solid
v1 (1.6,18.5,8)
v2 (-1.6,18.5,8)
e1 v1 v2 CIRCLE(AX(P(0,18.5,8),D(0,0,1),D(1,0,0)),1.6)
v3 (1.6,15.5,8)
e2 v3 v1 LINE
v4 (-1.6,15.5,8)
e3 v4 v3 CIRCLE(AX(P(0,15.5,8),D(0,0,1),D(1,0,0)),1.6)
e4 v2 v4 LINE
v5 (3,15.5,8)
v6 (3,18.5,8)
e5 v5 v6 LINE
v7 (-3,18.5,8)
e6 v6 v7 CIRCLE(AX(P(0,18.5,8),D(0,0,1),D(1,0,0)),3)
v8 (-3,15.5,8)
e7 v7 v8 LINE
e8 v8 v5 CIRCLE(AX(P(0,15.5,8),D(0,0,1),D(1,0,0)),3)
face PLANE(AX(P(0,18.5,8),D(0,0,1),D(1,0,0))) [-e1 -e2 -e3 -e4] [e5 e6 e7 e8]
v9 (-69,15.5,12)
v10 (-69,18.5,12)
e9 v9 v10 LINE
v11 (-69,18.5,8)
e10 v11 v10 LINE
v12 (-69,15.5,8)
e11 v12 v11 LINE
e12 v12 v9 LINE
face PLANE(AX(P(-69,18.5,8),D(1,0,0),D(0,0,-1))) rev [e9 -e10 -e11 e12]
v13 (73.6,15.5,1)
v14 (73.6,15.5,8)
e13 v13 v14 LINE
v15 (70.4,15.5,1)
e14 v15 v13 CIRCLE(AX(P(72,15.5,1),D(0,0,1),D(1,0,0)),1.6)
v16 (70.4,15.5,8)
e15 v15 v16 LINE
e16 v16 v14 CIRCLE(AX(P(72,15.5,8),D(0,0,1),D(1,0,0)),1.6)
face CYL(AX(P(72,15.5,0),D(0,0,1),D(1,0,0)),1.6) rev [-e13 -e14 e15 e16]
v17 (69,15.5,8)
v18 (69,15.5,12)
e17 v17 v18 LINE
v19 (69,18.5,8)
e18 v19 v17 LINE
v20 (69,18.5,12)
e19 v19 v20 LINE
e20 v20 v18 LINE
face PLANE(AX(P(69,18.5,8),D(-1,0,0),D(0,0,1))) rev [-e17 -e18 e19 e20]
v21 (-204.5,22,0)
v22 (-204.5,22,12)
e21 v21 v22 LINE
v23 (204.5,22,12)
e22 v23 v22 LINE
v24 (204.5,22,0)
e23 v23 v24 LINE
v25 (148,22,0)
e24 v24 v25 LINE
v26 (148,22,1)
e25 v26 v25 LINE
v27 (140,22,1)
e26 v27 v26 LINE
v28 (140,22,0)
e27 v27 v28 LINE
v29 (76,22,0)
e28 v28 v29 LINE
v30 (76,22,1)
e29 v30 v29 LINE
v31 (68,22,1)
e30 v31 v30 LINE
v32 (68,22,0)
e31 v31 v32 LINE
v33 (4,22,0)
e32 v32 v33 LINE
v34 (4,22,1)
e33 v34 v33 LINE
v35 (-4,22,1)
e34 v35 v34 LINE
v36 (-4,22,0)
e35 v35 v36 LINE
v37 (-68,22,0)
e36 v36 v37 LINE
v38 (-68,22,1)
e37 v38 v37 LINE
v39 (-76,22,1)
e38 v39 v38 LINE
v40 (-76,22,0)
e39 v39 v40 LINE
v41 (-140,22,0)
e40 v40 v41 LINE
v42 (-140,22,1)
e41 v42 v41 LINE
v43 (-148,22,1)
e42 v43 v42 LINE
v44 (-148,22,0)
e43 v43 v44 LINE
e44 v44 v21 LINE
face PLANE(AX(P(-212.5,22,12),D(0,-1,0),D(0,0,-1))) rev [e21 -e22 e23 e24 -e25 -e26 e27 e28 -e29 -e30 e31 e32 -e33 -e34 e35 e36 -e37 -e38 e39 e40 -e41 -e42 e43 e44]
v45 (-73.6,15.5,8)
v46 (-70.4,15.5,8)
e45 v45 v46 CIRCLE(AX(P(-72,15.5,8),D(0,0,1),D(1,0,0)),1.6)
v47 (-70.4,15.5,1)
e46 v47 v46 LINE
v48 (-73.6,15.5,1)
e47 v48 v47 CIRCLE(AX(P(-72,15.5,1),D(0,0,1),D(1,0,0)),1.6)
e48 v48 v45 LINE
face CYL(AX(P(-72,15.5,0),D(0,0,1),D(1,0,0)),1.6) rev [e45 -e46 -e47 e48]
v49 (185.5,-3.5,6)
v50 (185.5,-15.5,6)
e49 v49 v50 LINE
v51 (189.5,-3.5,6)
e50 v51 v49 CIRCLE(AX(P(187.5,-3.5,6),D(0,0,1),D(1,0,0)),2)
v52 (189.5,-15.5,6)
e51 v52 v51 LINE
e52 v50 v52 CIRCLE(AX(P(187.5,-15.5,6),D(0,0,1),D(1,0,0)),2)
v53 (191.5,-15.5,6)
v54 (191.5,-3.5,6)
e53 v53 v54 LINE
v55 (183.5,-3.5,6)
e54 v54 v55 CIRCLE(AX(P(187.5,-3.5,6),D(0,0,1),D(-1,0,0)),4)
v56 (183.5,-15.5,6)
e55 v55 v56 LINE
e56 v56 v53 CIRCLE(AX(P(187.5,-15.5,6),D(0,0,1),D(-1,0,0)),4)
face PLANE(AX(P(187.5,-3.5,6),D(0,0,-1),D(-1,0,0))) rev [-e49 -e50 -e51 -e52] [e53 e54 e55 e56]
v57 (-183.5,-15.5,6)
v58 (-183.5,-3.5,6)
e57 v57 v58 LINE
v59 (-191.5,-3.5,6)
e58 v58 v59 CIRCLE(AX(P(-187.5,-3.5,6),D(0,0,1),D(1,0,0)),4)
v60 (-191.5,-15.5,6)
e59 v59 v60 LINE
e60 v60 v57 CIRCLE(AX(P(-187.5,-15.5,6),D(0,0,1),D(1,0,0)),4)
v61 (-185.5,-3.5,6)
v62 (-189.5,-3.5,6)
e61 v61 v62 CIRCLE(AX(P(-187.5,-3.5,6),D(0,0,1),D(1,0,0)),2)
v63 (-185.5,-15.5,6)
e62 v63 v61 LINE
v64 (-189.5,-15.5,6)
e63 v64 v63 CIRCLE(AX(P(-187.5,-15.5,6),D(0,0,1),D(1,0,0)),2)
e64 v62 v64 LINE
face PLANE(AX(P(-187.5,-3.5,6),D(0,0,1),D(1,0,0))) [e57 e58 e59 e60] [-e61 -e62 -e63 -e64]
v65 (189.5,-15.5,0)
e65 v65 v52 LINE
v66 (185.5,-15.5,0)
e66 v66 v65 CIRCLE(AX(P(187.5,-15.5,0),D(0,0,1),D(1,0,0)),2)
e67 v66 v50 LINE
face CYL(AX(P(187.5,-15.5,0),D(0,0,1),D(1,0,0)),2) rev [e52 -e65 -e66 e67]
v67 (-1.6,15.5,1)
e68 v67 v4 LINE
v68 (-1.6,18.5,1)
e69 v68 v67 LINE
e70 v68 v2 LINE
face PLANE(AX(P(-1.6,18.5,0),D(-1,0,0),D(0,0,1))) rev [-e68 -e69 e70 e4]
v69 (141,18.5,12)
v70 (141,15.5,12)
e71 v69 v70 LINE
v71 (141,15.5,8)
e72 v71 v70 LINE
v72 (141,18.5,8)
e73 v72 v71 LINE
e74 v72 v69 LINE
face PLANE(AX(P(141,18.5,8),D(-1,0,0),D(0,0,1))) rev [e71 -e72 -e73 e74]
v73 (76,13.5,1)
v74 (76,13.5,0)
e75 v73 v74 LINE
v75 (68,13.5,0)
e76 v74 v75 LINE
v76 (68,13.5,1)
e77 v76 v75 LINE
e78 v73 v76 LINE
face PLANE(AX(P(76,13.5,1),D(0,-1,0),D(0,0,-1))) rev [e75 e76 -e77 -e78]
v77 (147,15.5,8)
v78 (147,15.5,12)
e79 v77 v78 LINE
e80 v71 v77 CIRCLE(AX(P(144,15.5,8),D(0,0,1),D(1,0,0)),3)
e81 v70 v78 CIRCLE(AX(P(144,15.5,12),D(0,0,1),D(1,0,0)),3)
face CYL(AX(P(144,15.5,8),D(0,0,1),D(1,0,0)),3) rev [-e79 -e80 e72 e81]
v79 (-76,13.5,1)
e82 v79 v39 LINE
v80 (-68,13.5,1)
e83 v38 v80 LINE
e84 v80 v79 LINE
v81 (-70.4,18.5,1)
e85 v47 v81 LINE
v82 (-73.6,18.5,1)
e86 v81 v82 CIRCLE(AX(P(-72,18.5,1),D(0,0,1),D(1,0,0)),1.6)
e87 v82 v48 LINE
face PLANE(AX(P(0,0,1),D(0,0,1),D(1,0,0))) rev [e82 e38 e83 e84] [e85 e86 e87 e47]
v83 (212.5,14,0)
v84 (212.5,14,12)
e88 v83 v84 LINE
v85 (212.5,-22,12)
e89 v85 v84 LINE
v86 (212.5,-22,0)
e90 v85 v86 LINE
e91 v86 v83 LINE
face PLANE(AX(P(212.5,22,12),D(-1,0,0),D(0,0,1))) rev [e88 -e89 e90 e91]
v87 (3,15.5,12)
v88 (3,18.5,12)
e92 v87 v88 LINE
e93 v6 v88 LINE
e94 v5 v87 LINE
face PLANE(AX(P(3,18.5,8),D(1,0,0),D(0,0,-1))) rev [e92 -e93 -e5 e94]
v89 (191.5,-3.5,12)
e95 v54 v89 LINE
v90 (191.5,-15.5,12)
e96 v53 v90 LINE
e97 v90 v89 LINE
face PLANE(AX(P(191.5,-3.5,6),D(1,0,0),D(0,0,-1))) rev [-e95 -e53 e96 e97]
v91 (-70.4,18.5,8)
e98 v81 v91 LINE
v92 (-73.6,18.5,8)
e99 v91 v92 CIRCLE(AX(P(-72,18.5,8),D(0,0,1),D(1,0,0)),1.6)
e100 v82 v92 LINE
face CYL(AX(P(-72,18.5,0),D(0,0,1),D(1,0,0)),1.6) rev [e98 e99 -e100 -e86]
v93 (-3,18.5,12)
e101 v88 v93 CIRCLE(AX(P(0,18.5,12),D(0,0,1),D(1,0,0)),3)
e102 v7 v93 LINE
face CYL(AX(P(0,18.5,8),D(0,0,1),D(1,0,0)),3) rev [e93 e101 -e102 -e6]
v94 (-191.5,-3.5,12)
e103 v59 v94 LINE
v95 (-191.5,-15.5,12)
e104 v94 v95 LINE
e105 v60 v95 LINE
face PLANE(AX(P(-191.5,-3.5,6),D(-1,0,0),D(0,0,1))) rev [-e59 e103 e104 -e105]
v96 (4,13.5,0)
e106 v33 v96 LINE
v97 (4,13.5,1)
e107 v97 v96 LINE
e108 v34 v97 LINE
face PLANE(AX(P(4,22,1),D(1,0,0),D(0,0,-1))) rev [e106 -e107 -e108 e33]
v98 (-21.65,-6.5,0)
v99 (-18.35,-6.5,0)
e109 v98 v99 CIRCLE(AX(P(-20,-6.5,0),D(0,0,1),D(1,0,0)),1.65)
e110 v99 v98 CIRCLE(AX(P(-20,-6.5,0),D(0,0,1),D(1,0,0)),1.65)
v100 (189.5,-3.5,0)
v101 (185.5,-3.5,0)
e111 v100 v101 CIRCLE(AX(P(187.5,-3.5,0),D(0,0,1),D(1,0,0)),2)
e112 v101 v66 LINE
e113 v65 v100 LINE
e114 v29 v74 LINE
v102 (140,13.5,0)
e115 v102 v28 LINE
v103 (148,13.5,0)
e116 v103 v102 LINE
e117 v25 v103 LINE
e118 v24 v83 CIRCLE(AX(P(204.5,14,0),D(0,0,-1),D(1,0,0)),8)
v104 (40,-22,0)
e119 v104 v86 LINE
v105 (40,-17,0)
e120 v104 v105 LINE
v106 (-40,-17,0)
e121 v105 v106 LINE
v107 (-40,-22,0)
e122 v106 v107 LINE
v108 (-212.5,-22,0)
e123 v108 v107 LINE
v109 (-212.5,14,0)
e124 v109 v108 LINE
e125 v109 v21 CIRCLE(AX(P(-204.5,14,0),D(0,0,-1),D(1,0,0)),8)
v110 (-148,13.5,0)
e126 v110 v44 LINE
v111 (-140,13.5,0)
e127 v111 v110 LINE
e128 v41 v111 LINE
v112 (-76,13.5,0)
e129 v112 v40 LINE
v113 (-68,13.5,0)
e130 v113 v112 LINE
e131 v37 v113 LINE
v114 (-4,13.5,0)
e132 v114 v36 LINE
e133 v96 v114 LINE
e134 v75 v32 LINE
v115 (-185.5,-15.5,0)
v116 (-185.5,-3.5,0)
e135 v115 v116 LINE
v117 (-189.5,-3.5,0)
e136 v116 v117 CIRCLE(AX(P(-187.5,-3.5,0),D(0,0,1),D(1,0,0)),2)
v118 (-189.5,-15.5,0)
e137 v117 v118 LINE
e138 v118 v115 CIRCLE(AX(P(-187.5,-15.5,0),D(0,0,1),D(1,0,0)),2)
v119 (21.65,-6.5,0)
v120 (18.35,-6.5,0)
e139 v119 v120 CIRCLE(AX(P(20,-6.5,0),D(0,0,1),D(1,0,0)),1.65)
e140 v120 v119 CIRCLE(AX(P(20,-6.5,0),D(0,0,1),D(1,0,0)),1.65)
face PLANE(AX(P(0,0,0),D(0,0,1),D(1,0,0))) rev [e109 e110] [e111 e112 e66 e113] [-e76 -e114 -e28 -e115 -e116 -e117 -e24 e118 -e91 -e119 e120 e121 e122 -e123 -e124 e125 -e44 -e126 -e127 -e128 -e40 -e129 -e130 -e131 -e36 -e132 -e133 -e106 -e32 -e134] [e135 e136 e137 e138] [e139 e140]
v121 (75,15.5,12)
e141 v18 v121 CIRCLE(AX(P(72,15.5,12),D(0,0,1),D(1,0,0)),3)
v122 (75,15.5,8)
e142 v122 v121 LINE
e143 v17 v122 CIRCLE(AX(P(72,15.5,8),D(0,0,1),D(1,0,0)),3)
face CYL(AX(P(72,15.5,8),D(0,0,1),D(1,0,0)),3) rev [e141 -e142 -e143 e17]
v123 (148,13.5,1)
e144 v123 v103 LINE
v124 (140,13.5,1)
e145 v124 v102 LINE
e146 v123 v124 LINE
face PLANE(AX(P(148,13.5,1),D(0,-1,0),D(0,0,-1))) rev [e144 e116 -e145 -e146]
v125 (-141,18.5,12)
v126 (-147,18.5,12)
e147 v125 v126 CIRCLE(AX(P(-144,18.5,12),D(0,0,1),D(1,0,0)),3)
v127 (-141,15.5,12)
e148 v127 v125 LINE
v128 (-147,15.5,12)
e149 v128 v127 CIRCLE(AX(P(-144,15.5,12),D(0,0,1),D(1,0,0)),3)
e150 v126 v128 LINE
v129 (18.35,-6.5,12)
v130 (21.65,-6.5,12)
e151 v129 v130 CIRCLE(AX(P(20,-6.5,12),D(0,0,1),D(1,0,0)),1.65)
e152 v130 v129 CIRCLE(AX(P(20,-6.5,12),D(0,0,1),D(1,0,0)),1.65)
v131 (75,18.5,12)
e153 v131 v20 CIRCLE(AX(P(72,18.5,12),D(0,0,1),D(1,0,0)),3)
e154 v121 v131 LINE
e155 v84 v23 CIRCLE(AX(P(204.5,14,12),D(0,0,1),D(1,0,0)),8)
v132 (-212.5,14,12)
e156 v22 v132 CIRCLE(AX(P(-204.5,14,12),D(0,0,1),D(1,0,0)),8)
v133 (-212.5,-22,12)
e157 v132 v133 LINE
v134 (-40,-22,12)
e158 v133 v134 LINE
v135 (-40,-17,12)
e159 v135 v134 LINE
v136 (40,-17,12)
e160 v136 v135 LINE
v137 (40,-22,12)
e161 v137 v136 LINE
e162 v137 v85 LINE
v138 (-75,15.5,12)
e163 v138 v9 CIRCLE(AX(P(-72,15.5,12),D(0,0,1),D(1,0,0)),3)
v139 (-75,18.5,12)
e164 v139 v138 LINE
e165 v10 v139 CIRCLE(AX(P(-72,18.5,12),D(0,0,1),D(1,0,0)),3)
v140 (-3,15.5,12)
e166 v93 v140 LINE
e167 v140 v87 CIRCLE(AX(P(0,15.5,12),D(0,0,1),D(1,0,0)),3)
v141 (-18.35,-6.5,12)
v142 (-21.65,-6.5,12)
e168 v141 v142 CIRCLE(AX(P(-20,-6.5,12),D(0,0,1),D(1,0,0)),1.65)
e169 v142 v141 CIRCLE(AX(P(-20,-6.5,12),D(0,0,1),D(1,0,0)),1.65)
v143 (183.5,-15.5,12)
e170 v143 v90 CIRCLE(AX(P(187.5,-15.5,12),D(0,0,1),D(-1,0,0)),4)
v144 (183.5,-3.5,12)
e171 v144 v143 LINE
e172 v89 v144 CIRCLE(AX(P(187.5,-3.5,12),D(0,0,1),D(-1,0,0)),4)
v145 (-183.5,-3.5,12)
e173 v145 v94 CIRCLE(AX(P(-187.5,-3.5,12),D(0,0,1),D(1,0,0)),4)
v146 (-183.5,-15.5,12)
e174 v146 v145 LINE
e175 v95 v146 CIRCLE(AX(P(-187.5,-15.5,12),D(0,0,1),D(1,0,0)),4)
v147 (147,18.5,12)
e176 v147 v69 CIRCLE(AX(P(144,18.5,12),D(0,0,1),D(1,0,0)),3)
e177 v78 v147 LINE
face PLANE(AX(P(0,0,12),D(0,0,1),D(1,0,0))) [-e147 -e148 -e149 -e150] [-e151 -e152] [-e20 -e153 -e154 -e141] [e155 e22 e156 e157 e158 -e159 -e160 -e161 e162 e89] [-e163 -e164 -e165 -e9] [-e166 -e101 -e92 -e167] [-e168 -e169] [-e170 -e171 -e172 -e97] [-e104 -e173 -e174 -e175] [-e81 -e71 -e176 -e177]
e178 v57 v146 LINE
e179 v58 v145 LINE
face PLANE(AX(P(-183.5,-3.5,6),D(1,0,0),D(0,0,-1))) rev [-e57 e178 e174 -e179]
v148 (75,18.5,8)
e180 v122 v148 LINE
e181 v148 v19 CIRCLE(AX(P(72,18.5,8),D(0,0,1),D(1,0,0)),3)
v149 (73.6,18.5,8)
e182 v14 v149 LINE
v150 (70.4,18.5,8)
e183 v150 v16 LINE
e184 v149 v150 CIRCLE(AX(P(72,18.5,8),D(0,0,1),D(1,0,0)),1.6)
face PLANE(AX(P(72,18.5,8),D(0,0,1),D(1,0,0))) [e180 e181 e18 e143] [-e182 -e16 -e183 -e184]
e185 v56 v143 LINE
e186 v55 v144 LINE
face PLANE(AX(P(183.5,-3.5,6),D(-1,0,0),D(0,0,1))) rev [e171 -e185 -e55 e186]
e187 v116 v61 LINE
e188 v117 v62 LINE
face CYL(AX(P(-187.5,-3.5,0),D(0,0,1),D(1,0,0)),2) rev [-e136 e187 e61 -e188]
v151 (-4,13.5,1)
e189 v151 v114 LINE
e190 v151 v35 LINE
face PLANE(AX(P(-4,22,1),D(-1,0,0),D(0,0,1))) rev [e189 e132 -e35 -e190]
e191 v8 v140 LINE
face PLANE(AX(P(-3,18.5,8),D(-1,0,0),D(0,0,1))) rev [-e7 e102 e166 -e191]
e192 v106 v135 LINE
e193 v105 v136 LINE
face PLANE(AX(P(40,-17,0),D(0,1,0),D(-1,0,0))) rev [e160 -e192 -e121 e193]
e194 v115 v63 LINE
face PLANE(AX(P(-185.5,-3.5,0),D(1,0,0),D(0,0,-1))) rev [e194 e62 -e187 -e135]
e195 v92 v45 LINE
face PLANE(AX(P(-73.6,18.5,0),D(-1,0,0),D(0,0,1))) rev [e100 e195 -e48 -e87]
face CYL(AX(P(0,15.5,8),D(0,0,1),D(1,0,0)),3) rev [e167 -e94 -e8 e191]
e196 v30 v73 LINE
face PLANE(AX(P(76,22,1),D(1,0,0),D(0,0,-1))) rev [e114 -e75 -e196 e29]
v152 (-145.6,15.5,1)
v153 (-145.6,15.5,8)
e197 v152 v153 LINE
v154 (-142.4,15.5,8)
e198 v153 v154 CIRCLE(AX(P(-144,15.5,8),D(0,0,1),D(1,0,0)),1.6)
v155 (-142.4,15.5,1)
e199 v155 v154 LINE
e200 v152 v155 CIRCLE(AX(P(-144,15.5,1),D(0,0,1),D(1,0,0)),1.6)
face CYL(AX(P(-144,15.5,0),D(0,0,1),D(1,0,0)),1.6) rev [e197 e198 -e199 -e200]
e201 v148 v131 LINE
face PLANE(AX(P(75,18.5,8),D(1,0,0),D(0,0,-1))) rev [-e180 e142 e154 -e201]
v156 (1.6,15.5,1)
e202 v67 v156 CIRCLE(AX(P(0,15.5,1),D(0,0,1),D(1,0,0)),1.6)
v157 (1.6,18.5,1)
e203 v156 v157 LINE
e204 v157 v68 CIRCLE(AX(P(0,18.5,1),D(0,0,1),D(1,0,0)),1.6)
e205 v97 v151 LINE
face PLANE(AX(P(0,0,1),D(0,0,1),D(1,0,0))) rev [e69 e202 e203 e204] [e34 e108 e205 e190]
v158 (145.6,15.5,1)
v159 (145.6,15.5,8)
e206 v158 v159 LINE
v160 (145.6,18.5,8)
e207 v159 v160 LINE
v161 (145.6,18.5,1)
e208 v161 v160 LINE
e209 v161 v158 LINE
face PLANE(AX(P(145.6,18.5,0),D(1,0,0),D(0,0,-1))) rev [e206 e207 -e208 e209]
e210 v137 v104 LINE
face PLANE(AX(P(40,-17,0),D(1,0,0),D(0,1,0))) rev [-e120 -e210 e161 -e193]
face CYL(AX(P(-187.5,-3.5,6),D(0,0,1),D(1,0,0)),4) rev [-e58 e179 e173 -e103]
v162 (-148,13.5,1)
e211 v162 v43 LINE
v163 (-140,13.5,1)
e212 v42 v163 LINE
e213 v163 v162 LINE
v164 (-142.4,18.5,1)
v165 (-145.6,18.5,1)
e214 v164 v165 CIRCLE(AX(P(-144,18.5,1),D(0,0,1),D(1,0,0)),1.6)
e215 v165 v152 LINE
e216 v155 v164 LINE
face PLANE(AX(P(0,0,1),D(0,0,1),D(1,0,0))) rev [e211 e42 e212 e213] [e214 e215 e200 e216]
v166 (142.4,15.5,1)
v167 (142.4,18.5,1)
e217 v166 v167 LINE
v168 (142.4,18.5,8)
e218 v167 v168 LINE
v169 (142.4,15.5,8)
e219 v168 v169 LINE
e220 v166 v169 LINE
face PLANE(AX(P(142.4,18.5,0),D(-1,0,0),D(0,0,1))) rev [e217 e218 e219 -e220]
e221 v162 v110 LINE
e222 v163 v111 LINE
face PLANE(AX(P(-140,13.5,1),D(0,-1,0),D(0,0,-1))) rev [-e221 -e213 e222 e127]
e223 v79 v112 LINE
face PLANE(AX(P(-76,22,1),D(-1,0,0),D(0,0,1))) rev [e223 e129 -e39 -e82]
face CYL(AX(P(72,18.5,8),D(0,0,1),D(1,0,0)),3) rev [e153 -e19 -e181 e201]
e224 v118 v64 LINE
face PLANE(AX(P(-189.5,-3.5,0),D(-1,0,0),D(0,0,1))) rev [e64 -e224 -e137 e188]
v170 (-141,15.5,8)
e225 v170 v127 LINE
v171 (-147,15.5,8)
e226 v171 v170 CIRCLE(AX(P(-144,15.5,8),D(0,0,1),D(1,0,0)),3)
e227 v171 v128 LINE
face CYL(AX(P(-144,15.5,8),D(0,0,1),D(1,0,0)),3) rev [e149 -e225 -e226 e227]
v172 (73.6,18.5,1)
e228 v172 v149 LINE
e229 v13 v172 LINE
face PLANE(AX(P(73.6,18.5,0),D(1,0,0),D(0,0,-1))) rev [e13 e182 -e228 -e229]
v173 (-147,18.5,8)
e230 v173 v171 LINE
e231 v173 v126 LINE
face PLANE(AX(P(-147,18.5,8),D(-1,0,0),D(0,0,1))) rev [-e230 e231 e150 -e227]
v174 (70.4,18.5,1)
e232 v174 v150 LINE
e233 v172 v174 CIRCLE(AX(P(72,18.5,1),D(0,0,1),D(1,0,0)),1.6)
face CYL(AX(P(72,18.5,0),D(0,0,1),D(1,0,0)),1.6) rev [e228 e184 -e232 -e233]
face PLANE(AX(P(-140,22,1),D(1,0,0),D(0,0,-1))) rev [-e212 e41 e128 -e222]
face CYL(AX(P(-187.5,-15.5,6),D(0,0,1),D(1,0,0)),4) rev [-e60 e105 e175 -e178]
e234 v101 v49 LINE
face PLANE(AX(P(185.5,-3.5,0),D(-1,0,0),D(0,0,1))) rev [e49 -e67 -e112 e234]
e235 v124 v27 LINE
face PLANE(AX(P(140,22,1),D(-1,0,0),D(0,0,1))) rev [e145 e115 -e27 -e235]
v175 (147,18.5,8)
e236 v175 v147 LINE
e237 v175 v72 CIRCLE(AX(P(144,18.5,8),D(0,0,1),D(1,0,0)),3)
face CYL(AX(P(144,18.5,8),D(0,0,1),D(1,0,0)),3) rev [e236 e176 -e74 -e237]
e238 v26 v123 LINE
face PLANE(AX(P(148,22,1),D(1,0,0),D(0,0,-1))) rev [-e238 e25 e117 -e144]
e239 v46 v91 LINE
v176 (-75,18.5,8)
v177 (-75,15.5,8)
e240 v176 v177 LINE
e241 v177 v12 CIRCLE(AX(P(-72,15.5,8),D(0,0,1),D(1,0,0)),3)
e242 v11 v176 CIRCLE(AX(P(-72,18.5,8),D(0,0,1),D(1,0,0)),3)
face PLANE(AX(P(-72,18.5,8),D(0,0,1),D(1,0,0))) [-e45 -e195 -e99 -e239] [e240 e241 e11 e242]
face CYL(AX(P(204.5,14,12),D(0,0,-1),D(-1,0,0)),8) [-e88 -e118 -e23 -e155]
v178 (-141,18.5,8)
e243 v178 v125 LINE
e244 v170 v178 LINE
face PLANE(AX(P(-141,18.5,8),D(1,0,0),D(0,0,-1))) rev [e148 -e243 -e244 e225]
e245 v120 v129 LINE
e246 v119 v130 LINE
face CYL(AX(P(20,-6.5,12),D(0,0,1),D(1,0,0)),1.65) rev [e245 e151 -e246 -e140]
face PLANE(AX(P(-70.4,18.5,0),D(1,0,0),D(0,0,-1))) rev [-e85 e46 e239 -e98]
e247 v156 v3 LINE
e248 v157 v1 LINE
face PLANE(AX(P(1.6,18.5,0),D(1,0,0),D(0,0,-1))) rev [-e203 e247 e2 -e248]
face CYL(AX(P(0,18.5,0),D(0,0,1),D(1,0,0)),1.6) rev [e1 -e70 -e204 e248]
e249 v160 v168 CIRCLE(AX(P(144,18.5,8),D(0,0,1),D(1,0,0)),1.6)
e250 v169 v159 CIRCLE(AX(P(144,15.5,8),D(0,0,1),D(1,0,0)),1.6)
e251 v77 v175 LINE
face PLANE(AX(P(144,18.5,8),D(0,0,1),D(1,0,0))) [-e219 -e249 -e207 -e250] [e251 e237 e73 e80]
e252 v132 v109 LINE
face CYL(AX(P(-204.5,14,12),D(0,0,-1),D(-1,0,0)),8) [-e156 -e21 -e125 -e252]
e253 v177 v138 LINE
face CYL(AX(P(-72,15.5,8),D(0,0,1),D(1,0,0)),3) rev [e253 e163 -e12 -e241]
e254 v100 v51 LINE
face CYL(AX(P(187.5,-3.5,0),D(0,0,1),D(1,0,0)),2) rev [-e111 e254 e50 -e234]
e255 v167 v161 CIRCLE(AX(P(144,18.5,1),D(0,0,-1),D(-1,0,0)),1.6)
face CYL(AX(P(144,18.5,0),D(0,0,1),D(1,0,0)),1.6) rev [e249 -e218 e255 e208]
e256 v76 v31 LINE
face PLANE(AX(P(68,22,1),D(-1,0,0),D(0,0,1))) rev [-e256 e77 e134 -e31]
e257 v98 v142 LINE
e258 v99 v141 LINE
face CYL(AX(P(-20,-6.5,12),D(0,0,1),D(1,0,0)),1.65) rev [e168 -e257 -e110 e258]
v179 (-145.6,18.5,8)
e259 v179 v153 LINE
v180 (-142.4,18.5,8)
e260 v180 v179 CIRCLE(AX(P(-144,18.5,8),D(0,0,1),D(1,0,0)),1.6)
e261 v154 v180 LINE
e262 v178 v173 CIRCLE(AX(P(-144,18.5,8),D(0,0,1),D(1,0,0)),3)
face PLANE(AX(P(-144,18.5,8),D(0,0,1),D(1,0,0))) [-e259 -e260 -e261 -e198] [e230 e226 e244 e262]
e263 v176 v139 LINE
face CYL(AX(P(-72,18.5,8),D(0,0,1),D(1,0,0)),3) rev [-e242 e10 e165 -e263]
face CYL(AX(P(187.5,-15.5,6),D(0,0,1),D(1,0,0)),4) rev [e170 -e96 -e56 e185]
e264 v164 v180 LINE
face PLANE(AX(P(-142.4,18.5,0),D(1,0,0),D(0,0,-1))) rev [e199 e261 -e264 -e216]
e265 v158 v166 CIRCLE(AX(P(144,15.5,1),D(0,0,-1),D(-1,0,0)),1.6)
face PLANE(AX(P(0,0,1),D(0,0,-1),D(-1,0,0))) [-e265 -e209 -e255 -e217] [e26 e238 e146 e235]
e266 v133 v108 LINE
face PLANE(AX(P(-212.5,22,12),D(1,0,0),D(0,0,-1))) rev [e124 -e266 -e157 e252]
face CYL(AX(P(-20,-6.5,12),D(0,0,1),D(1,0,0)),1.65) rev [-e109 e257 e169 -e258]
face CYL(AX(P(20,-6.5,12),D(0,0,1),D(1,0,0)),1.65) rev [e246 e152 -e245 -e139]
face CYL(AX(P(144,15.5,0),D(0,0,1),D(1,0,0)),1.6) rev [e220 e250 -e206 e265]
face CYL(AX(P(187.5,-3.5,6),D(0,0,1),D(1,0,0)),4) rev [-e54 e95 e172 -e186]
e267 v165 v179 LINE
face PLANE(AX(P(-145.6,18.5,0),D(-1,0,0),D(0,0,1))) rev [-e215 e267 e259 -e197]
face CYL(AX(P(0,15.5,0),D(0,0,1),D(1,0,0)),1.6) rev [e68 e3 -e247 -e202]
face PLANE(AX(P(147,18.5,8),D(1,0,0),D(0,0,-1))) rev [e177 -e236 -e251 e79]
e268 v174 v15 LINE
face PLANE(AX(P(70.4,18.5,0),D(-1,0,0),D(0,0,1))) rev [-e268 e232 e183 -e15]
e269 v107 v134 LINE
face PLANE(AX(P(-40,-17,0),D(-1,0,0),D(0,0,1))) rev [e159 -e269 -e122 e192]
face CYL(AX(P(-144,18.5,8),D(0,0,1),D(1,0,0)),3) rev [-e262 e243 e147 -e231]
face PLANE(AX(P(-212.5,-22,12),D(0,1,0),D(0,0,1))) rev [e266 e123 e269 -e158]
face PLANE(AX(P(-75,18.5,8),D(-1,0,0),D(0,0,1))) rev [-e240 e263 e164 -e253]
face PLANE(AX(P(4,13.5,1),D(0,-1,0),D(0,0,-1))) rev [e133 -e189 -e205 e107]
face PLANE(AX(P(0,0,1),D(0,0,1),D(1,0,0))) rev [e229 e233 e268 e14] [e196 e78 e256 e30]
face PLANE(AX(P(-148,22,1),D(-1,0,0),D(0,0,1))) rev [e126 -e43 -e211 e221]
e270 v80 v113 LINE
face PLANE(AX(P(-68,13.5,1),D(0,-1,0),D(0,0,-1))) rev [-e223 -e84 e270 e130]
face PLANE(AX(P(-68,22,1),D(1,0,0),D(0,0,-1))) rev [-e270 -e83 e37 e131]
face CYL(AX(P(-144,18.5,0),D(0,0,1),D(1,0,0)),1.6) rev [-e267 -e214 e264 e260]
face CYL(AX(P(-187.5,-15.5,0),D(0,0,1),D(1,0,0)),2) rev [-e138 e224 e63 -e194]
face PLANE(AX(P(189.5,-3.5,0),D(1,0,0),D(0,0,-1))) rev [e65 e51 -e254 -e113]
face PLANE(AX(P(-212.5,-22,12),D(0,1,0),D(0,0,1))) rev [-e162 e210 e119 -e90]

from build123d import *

# Parameters (mm, degrees)
SKETCH_1_W             = 425
SKETCH_1_H             = 44
EXTRUDE_1_DEPTH        = 12
FILLET_1_R             = 8
CUT_EXTRUDE_1_DEPTH    = 6
CUT_EXTRUDE_2_DEPTH    = 214.720027138
SKETCH_8_W             = 80
SKETCH_8_H             = 35.518481864
CUT_EXTRUDE_3_DEPTH    = 214.972544968
SKETCH_10_W            = 8
SKETCH_10_H            = 8.5
CUT_EXTRUDE_4_DEPTH    = 1
CUT_EXTRUDE_5_DEPTH    = 4
CUT_EXTRUDE_6_DEPTH    = 214.785523364
PATTERN_LINEAR_1_COUNT = 5
PATTERN_LINEAR_1_PITCH = 72
HOLE_WIZARD_M4_1_D     = 3.3


with BuildPart() as part:
    # 草图1 → 凸台-拉伸1 (new body)
    with BuildSketch(Plane.XY):
        Rectangle(SKETCH_1_W, SKETCH_1_H)
    extrude(amount=EXTRUDE_1_DEPTH)

    # 圆角1
    fillet_1_edges = [part.edges().sort_by_distance(p)[0] for p in [
        (-212.5, 22, 6),
        (212.5, 22, 6),
    ]]
    fillet(fillet_1_edges, radius=FILLET_1_R)

    # 草图2 → 切除-拉伸1 (cut)
    with BuildSketch(Plane.XY.offset(12)):
        with BuildLine():
            Line((-183.5, -3.5), (-183.5, -15.5))
            ThreePointArc((-183.5, -15.5), (-187.5, -19.5), (-191.5, -15.5))
            Line((-191.5, -15.5), (-191.5, -3.5))
            ThreePointArc((-191.5, -3.5), (-187.5, 0.5), (-183.5, -3.5))
        make_face()
        with BuildLine():
            Line((183.5, -3.5), (183.5, -15.5))
            ThreePointArc((183.5, -15.5), (187.5, -19.5), (191.5, -15.5))
            Line((191.5, -15.5), (191.5, -3.5))
            ThreePointArc((191.5, -3.5), (187.5, 0.5), (183.5, -3.5))
        make_face()
    extrude(amount=-CUT_EXTRUDE_1_DEPTH, mode=Mode.SUBTRACT)

    # 草图3 → 切除-拉伸2 (cut, through all)
    with BuildSketch(Plane.XY.offset(6)):
        with BuildLine():
            Line((-185.5, -3.5), (-185.5, -15.5))
            ThreePointArc((-185.5, -15.5), (-187.5, -17.5), (-189.5, -15.5))
            Line((-189.5, -15.5), (-189.5, -3.5))
            ThreePointArc((-189.5, -3.5), (-187.5, -1.5), (-185.5, -3.5))
        make_face()
        with BuildLine():
            Line((189.5, -3.5), (189.5, -15.5))
            ThreePointArc((189.5, -15.5), (187.5, -17.5), (185.5, -15.5))
            Line((185.5, -15.5), (185.5, -3.5))
            ThreePointArc((185.5, -3.5), (187.5, -1.5), (189.5, -3.5))
        make_face()
    extrude(amount=-CUT_EXTRUDE_2_DEPTH, mode=Mode.SUBTRACT)

    # 草图8 → 切除-拉伸3 (cut, through all)
    with BuildSketch(Plane.XY.offset(12)):
        with Locations((0, -34.759240932)):
            Rectangle(SKETCH_8_W, SKETCH_8_H)
    extrude(amount=-CUT_EXTRUDE_3_DEPTH, mode=Mode.SUBTRACT)

    # 草图10 → 切除-拉伸4 (cut)
    with BuildSketch(Plane(origin=(0, 0, 0), x_dir=(-1, 0, 0), z_dir=(0, 0, -1))):
        with Locations((-144, 17.75)):
            Rectangle(SKETCH_10_W, SKETCH_10_H)
        with Locations((-72, 17.75)):
            Rectangle(SKETCH_10_W, SKETCH_10_H)
        with Locations((0, 17.75)):
            Rectangle(SKETCH_10_W, SKETCH_10_H)
        with Locations((72, 17.75)):
            Rectangle(SKETCH_10_W, SKETCH_10_H)
        with Locations((144, 17.75)):
            Rectangle(SKETCH_10_W, SKETCH_10_H)
    extrude(amount=-CUT_EXTRUDE_4_DEPTH, mode=Mode.SUBTRACT)

    # 草图11 → 切除-拉伸5 (cut)
    with BuildSketch(Plane.XY.offset(12)):
        with BuildLine():
            Line((-141, 18.5), (-141, 15.5))
            ThreePointArc((-141, 15.5), (-144, 12.5), (-147, 15.5))
            Line((-147, 15.5), (-147, 18.5))
            ThreePointArc((-147, 18.5), (-144, 21.5), (-141, 18.5))
        make_face()
    cut_extrude_5 = extrude(amount=-CUT_EXTRUDE_5_DEPTH, mode=Mode.SUBTRACT)

    # 草图12 → 切除-拉伸6 (cut, through all)
    with BuildSketch(Plane.XY.offset(8)):
        with BuildLine():
            Line((-142.4, 18.5), (-142.4, 15.5))
            ThreePointArc((-142.4, 15.5), (-144, 13.9), (-145.6, 15.5))
            Line((-145.6, 15.5), (-145.6, 18.5))
            ThreePointArc((-145.6, 18.5), (-144, 20.1), (-142.4, 18.5))
        make_face()
    cut_extrude_6 = extrude(amount=-CUT_EXTRUDE_6_DEPTH, mode=Mode.SUBTRACT)

    # 阵列(线性)1: 切除-拉伸5, 切除-拉伸6 ×5
    with Locations(*[(i * PATTERN_LINEAR_1_PITCH, 0, 0) for i in range(1, PATTERN_LINEAR_1_COUNT)]):
        add(cut_extrude_5, mode=Mode.SUBTRACT)
        add(cut_extrude_6, mode=Mode.SUBTRACT)

    # M4 螺纹孔1 (through all)
    with Locations(Plane.XY.offset(12)):
        with Locations((-20, -6.5), (20, -6.5)):
            Hole(HOLE_WIZARD_M4_1_D / 2)


solid = part.part
